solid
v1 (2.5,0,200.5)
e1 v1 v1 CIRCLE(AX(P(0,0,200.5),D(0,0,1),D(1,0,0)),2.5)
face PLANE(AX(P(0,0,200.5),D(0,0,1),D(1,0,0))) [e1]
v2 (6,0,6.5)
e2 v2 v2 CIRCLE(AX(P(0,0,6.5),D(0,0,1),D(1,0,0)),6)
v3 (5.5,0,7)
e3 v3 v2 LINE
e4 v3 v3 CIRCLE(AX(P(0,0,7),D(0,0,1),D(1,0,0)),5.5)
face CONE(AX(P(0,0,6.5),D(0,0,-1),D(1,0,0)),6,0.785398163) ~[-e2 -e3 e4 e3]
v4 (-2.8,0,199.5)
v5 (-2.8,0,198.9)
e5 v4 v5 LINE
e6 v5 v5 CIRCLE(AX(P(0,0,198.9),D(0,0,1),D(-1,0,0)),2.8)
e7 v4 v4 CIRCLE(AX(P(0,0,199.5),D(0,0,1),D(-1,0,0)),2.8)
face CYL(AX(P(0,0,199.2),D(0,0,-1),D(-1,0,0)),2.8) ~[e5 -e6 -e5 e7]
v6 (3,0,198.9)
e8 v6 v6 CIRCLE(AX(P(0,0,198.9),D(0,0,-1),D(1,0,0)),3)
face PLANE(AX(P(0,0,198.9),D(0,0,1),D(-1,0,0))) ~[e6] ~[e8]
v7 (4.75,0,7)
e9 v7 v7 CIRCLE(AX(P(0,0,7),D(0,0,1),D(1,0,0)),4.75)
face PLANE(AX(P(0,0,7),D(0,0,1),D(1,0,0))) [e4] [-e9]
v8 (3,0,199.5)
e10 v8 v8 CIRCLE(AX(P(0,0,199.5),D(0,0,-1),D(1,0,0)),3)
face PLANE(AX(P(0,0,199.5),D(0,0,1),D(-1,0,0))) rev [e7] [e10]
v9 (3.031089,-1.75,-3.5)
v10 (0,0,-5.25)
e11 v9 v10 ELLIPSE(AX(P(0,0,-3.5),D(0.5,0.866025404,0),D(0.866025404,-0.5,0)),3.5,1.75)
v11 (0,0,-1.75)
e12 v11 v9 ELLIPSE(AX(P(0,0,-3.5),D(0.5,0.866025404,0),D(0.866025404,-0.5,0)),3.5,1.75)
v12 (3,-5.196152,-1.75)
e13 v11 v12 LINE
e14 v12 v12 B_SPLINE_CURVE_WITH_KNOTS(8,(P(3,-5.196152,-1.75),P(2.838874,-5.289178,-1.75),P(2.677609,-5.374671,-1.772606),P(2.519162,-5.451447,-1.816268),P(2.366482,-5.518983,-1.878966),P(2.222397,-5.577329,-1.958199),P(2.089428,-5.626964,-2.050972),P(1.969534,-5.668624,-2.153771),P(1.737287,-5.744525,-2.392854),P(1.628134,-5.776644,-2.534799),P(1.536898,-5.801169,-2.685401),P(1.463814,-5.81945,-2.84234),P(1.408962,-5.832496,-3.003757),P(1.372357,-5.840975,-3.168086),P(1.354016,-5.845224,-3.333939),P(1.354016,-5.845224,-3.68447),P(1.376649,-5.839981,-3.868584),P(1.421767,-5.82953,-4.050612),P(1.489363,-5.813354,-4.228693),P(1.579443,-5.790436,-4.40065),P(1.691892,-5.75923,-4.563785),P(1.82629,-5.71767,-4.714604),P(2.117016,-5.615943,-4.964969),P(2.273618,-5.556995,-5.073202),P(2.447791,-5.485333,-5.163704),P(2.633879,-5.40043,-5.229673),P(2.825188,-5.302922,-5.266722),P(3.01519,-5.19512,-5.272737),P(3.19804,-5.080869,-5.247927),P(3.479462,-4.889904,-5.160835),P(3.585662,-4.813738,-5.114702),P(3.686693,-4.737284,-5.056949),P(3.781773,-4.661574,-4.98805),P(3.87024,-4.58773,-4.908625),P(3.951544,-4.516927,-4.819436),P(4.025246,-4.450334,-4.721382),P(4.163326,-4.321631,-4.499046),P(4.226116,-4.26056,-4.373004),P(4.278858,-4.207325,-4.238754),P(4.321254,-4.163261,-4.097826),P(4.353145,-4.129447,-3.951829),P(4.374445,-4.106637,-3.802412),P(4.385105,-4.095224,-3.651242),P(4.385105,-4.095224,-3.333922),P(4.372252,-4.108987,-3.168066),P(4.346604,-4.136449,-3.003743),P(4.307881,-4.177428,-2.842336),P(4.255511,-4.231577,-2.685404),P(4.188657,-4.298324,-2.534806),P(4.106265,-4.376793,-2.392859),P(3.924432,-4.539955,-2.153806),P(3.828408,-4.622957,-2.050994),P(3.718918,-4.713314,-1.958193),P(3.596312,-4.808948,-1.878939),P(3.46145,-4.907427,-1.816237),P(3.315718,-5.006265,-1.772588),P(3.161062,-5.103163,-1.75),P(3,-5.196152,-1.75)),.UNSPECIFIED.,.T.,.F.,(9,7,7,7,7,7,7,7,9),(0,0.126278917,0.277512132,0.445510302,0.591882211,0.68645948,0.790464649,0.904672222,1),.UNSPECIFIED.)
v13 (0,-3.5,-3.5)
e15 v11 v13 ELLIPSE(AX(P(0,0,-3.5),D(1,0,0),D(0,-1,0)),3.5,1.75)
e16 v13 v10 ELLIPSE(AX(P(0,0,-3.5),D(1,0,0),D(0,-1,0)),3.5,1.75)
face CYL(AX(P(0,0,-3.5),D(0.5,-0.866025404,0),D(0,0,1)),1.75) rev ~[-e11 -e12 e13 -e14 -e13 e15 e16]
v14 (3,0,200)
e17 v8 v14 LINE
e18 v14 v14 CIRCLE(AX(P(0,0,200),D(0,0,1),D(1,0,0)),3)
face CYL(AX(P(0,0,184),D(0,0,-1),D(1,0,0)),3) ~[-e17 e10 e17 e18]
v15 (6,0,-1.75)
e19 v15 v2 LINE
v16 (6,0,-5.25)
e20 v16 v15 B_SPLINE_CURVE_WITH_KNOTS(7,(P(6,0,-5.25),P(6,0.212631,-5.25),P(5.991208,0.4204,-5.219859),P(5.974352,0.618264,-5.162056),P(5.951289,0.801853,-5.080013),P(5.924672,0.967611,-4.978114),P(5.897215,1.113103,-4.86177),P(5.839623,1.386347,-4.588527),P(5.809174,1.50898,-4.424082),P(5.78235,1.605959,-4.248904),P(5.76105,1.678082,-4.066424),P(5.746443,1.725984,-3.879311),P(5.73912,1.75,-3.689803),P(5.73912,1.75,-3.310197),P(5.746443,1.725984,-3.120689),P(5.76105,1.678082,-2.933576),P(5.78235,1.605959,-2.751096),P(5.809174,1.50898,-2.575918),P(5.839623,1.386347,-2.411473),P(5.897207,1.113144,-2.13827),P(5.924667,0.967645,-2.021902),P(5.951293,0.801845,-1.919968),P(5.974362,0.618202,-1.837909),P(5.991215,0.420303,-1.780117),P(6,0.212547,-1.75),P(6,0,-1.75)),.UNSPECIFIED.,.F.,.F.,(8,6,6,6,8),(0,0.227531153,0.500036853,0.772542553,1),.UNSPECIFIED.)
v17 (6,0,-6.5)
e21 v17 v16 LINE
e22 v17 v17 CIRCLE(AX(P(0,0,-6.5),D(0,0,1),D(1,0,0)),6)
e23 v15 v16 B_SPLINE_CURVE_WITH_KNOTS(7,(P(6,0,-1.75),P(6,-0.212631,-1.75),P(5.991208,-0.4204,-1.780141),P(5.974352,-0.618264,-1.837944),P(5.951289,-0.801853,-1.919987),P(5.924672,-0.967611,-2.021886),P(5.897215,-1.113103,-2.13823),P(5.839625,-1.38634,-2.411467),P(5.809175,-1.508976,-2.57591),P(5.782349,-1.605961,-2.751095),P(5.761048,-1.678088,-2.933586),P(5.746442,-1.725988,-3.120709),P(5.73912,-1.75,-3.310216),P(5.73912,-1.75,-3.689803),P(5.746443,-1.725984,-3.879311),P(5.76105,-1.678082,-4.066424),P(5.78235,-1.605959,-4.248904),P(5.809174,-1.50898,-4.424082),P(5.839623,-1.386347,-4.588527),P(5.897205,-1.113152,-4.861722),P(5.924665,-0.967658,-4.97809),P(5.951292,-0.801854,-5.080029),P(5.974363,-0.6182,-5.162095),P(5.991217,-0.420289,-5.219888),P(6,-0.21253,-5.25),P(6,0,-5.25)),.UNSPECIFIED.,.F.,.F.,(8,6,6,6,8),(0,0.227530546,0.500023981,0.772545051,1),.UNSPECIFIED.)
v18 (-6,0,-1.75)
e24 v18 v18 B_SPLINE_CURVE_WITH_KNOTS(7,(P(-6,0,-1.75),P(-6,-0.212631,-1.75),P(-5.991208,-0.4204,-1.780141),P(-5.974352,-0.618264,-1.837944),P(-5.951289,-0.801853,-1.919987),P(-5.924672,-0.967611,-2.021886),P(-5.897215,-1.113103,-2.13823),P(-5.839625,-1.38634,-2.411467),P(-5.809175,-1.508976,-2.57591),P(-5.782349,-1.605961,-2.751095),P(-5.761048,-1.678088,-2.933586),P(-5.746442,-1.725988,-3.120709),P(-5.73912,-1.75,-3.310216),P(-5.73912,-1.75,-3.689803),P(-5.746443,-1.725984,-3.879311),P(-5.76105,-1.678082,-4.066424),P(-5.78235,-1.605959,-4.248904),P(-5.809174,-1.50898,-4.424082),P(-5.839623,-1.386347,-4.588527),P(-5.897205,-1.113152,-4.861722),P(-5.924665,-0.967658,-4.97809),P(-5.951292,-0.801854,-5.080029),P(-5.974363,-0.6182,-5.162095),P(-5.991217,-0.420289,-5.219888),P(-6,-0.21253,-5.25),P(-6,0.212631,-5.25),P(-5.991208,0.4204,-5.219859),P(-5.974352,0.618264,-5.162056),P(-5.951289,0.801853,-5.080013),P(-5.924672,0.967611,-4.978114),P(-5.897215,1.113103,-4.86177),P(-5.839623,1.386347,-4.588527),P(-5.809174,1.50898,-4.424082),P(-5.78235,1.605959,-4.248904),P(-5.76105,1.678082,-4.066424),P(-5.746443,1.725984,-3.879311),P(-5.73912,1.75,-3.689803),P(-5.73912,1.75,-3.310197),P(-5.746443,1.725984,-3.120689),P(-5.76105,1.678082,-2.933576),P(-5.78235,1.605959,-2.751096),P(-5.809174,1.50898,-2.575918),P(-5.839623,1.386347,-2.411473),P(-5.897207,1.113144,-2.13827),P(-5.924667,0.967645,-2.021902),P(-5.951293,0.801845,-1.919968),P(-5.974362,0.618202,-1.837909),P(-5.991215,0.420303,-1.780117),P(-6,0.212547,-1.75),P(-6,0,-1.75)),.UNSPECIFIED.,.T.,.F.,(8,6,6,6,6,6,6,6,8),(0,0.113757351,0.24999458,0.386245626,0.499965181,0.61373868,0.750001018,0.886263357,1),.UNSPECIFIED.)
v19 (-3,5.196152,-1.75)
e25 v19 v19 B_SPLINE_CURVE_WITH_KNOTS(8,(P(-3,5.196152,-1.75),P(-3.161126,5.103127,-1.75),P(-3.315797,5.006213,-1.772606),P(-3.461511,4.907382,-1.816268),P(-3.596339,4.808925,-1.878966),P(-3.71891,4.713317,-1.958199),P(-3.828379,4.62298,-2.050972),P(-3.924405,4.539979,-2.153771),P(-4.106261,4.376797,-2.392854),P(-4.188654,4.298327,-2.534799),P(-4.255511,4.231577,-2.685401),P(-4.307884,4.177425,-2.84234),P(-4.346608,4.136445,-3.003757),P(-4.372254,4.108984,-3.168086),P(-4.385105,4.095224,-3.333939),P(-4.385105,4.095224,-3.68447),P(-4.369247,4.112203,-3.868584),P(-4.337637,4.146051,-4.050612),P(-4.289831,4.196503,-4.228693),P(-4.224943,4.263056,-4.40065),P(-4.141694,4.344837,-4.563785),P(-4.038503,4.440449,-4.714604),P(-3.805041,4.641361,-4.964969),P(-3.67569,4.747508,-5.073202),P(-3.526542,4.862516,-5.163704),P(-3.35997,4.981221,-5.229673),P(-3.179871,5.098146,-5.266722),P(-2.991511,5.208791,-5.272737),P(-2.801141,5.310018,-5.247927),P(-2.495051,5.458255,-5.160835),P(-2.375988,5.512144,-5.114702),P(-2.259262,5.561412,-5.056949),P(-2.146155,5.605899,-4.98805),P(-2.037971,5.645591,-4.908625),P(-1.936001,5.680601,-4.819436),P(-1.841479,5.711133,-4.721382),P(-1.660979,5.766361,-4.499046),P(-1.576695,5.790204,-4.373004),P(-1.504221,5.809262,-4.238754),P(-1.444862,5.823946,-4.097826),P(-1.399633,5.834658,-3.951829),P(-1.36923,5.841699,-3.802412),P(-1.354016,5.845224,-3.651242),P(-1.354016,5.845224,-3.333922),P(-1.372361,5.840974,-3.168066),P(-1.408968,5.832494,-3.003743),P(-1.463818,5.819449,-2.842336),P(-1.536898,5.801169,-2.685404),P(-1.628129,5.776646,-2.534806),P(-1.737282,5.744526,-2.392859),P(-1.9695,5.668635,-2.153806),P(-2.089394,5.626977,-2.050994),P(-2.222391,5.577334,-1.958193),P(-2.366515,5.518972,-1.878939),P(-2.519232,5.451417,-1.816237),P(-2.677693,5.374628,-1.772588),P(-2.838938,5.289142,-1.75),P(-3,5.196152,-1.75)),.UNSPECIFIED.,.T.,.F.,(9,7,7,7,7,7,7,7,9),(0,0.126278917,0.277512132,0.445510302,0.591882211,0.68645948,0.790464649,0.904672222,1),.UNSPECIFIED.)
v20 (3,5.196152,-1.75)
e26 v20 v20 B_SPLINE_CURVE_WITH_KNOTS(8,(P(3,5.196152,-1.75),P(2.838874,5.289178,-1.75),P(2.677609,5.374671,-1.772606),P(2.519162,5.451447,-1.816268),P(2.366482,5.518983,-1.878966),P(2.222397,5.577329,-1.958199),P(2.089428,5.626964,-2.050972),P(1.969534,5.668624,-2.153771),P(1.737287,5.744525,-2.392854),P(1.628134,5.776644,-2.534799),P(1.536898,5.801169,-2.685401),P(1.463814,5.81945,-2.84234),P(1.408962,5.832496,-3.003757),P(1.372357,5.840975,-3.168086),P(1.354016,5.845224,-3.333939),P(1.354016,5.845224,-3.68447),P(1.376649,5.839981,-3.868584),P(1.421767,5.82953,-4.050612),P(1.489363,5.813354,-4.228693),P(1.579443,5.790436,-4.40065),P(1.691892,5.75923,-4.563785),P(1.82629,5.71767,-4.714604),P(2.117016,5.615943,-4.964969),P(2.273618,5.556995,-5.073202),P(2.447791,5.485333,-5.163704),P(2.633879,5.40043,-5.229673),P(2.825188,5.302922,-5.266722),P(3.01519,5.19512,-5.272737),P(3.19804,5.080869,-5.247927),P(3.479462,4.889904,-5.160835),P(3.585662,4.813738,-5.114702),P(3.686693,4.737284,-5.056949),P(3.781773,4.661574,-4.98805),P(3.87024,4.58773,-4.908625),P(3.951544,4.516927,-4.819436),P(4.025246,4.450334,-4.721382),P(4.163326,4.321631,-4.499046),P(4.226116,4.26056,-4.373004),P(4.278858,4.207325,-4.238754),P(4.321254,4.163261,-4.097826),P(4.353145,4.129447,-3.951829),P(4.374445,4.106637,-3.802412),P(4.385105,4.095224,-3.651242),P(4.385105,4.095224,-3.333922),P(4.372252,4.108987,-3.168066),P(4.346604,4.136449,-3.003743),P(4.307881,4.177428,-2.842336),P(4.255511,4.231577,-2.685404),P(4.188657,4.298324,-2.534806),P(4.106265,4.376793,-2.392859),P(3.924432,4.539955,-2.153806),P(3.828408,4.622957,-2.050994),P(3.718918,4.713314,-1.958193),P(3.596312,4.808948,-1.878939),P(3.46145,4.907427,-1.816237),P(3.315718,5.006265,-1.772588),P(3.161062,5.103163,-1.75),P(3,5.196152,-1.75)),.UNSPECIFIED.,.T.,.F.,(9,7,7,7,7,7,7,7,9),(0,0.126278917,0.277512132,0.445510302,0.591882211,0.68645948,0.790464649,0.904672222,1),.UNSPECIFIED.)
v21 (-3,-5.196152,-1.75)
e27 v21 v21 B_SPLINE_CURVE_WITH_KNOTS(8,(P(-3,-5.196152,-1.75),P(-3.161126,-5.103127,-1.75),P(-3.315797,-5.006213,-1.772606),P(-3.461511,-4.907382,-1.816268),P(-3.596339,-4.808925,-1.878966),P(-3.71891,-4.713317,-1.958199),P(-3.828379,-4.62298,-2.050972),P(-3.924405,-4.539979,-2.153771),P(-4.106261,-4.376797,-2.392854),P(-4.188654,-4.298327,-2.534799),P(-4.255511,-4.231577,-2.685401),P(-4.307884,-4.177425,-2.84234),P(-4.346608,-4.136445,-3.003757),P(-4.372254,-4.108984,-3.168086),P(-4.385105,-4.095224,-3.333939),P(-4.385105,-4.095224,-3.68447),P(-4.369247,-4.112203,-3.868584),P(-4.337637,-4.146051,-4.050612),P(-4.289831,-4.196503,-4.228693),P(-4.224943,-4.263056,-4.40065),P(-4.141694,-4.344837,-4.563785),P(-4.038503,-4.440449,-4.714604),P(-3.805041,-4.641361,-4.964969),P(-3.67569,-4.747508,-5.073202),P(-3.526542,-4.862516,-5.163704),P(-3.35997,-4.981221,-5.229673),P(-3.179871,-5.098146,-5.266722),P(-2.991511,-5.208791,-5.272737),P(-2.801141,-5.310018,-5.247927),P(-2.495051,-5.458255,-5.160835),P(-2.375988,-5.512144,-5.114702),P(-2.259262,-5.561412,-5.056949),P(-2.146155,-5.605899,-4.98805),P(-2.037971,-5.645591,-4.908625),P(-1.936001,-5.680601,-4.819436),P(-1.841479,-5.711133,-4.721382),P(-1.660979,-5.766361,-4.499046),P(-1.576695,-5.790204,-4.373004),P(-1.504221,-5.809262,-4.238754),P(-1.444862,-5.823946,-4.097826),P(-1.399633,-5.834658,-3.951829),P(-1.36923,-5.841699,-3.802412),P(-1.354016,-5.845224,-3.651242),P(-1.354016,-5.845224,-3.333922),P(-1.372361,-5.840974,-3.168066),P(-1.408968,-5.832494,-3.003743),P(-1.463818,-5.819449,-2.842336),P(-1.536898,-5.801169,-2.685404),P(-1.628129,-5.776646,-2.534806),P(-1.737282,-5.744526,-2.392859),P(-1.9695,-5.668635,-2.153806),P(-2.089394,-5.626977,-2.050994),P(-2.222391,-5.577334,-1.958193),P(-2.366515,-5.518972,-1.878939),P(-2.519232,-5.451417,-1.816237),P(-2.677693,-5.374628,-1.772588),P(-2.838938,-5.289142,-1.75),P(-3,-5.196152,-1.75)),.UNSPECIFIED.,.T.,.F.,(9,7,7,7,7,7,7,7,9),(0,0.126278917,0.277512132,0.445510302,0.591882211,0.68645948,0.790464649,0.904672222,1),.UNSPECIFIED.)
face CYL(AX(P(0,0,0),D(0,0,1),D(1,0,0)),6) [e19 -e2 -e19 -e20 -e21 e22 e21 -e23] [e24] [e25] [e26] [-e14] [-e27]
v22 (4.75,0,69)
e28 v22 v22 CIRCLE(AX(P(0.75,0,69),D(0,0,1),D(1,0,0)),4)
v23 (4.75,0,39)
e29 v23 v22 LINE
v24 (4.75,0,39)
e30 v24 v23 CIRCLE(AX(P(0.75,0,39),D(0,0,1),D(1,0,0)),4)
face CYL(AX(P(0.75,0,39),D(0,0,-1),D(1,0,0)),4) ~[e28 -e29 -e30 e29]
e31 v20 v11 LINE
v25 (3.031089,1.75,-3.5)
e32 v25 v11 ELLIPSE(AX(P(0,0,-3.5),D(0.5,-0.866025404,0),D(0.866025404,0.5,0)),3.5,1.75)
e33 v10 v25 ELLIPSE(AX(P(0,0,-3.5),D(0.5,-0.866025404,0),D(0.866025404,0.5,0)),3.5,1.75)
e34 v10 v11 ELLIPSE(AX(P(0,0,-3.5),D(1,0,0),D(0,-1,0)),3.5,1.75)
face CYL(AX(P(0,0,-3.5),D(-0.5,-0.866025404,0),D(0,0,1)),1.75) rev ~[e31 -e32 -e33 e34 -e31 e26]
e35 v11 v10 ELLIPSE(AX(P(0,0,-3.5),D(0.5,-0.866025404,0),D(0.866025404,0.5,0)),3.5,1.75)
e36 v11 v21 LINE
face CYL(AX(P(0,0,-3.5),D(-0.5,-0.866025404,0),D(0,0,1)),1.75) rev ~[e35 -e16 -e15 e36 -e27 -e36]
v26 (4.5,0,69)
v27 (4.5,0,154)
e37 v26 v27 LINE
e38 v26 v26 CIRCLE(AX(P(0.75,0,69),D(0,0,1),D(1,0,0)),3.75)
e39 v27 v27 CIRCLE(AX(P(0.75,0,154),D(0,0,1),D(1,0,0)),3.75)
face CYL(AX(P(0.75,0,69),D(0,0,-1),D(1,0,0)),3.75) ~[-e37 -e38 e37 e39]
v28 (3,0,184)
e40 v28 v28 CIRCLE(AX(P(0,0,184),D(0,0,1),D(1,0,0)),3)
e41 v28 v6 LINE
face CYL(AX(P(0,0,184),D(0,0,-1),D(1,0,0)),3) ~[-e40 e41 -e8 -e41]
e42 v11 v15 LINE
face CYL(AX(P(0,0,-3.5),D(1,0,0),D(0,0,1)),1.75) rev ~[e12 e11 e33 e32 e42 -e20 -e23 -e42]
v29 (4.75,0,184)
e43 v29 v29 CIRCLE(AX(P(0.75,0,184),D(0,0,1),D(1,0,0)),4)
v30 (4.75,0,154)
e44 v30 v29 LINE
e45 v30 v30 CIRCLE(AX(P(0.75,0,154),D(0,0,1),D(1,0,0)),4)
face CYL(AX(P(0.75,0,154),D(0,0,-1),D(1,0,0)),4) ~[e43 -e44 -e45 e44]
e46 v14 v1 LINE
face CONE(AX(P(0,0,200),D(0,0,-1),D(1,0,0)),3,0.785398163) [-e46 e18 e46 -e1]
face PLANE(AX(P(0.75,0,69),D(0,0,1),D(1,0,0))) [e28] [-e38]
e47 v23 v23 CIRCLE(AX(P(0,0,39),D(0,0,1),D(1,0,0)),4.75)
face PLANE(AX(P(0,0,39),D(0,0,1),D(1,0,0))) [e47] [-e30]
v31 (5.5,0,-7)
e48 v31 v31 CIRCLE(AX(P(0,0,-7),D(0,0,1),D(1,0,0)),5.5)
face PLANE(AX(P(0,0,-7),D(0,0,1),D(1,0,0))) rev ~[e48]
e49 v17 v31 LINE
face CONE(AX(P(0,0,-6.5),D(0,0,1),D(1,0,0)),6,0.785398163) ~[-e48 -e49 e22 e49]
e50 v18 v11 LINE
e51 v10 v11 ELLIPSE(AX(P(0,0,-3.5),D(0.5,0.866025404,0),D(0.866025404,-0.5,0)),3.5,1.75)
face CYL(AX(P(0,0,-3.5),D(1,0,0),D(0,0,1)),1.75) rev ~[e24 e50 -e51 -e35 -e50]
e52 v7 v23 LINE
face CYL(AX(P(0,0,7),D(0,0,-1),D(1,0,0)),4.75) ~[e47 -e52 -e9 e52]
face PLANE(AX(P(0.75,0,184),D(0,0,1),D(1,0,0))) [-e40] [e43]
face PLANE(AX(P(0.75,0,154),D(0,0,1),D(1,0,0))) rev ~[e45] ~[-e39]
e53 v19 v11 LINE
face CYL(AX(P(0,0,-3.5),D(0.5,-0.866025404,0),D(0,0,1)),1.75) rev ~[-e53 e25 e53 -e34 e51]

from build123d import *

# Parameters (mm, degrees)
SKETCH1_R           = 6
BOSS_EXTRUDE1_DEPTH = 7
SKETCH2_R           = 4.75
BOSS_EXTRUDE2_DEPTH = 32
SKETCH3_R           = 4
BOSS_EXTRUDE3_DEPTH = 30
SKETCH4_R           = 3.75
BOSS_EXTRUDE4_DEPTH = 85
SKETCH5_R           = 4
BOSS_EXTRUDE5_DEPTH = 30
SKETCH6_R           = 3
BOSS_EXTRUDE6_DEPTH = 16.5
SKETCH8_W           = 1.531468115
SKETCH8_H           = 0.6
CHAMFER1_SIZE       = 0.5
SKETCH11_R          = 1.75
CUT_EXTRUDE1_DEPTH  = 11.5
CIRPATTERN1_COUNT   = 3
CIRPATTERN1_ANGLE   = 120
CHAMFER2_SIZE       = 0.5


with BuildPart() as part:
    # Sketch1 → Boss-Extrude1 (new, symmetric)
    with BuildSketch(Plane.XY):
        Circle(SKETCH1_R)
    extrude(amount=BOSS_EXTRUDE1_DEPTH, both=True)

    # Sketch2 → Boss-Extrude2 (add)
    with BuildSketch(Plane.XY.offset(7)):
        Circle(SKETCH2_R)
    extrude(amount=BOSS_EXTRUDE2_DEPTH)

    # Sketch3 → Boss-Extrude3 (add)
    with BuildSketch(Plane.XY.offset(39)):
        with Locations((0.75, 0)):
            Circle(SKETCH3_R)
    extrude(amount=BOSS_EXTRUDE3_DEPTH)

    # Sketch4 → Boss-Extrude4 (add)
    with BuildSketch(Plane.XY.offset(69)):
        with Locations((0.75, 0)):
            Circle(SKETCH4_R)
    extrude(amount=BOSS_EXTRUDE4_DEPTH)

    # Sketch5 → Boss-Extrude5 (add)
    with BuildSketch(Plane.XY.offset(154)):
        with Locations((0.75, 0)):
            Circle(SKETCH5_R)
    extrude(amount=BOSS_EXTRUDE5_DEPTH)

    # Sketch6 → Boss-Extrude6 (add)
    with BuildSketch(Plane.XY.offset(184)):
        Circle(SKETCH6_R)
    extrude(amount=BOSS_EXTRUDE6_DEPTH)

    # Sketch8 → Cut-Revolve1 (revolve, cut)
    with BuildSketch(Plane(origin=(0, 0, 0), x_dir=(1, 0, 0), z_dir=(0, 1, 0)), mode=Mode.PRIVATE) as cut_revolve1_sk:
        with Locations((3.565734058, -199.2)):
            Rectangle(SKETCH8_W, SKETCH8_H)
    revolve(cut_revolve1_sk.sketch.rotate(Axis((0, 0, 0), (0, 0, 1)), 180), axis=Axis((0, 0, 0), (0, 0, 1)), mode=Mode.SUBTRACT)

    # Chamfer1
    chamfer1_edges = [part.edges().sort_by_distance(p)[0] for p in [
        (-6, 0, -7),
        (-6, 0, 7),
    ]]
    chamfer(chamfer1_edges, length=CHAMFER1_SIZE)

    # Sketch11 → Cut-Extrude1 (cut, symmetric)
    with BuildSketch(Plane(origin=(0, 0, 0), x_dir=(0, 0, -1), z_dir=(1, 0, 0))):
        with Locations(Location((3.5, 0, 0), (0, 0, 180))):
            Circle(SKETCH11_R)
    cut_extrude1 = extrude(amount=CUT_EXTRUDE1_DEPTH, both=True, mode=Mode.SUBTRACT)

    # CirPattern1: Cut-Extrude1 ×3 about axis
    cirpattern1_axis = Axis((0, 0, 7), (0, 0, -1))
    for i in range(1, CIRPATTERN1_COUNT):
        add(cut_extrude1.rotate(cirpattern1_axis, i * CIRPATTERN1_ANGLE / (CIRPATTERN1_COUNT - 1)), mode=Mode.SUBTRACT)

    # Chamfer2
    chamfer2_edges = [part.edges().sort_by_distance(p)[0] for p in [
        (-3, 0, 200.5),
    ]]
    chamfer(chamfer2_edges, length=CHAMFER2_SIZE)


solid = part.part
